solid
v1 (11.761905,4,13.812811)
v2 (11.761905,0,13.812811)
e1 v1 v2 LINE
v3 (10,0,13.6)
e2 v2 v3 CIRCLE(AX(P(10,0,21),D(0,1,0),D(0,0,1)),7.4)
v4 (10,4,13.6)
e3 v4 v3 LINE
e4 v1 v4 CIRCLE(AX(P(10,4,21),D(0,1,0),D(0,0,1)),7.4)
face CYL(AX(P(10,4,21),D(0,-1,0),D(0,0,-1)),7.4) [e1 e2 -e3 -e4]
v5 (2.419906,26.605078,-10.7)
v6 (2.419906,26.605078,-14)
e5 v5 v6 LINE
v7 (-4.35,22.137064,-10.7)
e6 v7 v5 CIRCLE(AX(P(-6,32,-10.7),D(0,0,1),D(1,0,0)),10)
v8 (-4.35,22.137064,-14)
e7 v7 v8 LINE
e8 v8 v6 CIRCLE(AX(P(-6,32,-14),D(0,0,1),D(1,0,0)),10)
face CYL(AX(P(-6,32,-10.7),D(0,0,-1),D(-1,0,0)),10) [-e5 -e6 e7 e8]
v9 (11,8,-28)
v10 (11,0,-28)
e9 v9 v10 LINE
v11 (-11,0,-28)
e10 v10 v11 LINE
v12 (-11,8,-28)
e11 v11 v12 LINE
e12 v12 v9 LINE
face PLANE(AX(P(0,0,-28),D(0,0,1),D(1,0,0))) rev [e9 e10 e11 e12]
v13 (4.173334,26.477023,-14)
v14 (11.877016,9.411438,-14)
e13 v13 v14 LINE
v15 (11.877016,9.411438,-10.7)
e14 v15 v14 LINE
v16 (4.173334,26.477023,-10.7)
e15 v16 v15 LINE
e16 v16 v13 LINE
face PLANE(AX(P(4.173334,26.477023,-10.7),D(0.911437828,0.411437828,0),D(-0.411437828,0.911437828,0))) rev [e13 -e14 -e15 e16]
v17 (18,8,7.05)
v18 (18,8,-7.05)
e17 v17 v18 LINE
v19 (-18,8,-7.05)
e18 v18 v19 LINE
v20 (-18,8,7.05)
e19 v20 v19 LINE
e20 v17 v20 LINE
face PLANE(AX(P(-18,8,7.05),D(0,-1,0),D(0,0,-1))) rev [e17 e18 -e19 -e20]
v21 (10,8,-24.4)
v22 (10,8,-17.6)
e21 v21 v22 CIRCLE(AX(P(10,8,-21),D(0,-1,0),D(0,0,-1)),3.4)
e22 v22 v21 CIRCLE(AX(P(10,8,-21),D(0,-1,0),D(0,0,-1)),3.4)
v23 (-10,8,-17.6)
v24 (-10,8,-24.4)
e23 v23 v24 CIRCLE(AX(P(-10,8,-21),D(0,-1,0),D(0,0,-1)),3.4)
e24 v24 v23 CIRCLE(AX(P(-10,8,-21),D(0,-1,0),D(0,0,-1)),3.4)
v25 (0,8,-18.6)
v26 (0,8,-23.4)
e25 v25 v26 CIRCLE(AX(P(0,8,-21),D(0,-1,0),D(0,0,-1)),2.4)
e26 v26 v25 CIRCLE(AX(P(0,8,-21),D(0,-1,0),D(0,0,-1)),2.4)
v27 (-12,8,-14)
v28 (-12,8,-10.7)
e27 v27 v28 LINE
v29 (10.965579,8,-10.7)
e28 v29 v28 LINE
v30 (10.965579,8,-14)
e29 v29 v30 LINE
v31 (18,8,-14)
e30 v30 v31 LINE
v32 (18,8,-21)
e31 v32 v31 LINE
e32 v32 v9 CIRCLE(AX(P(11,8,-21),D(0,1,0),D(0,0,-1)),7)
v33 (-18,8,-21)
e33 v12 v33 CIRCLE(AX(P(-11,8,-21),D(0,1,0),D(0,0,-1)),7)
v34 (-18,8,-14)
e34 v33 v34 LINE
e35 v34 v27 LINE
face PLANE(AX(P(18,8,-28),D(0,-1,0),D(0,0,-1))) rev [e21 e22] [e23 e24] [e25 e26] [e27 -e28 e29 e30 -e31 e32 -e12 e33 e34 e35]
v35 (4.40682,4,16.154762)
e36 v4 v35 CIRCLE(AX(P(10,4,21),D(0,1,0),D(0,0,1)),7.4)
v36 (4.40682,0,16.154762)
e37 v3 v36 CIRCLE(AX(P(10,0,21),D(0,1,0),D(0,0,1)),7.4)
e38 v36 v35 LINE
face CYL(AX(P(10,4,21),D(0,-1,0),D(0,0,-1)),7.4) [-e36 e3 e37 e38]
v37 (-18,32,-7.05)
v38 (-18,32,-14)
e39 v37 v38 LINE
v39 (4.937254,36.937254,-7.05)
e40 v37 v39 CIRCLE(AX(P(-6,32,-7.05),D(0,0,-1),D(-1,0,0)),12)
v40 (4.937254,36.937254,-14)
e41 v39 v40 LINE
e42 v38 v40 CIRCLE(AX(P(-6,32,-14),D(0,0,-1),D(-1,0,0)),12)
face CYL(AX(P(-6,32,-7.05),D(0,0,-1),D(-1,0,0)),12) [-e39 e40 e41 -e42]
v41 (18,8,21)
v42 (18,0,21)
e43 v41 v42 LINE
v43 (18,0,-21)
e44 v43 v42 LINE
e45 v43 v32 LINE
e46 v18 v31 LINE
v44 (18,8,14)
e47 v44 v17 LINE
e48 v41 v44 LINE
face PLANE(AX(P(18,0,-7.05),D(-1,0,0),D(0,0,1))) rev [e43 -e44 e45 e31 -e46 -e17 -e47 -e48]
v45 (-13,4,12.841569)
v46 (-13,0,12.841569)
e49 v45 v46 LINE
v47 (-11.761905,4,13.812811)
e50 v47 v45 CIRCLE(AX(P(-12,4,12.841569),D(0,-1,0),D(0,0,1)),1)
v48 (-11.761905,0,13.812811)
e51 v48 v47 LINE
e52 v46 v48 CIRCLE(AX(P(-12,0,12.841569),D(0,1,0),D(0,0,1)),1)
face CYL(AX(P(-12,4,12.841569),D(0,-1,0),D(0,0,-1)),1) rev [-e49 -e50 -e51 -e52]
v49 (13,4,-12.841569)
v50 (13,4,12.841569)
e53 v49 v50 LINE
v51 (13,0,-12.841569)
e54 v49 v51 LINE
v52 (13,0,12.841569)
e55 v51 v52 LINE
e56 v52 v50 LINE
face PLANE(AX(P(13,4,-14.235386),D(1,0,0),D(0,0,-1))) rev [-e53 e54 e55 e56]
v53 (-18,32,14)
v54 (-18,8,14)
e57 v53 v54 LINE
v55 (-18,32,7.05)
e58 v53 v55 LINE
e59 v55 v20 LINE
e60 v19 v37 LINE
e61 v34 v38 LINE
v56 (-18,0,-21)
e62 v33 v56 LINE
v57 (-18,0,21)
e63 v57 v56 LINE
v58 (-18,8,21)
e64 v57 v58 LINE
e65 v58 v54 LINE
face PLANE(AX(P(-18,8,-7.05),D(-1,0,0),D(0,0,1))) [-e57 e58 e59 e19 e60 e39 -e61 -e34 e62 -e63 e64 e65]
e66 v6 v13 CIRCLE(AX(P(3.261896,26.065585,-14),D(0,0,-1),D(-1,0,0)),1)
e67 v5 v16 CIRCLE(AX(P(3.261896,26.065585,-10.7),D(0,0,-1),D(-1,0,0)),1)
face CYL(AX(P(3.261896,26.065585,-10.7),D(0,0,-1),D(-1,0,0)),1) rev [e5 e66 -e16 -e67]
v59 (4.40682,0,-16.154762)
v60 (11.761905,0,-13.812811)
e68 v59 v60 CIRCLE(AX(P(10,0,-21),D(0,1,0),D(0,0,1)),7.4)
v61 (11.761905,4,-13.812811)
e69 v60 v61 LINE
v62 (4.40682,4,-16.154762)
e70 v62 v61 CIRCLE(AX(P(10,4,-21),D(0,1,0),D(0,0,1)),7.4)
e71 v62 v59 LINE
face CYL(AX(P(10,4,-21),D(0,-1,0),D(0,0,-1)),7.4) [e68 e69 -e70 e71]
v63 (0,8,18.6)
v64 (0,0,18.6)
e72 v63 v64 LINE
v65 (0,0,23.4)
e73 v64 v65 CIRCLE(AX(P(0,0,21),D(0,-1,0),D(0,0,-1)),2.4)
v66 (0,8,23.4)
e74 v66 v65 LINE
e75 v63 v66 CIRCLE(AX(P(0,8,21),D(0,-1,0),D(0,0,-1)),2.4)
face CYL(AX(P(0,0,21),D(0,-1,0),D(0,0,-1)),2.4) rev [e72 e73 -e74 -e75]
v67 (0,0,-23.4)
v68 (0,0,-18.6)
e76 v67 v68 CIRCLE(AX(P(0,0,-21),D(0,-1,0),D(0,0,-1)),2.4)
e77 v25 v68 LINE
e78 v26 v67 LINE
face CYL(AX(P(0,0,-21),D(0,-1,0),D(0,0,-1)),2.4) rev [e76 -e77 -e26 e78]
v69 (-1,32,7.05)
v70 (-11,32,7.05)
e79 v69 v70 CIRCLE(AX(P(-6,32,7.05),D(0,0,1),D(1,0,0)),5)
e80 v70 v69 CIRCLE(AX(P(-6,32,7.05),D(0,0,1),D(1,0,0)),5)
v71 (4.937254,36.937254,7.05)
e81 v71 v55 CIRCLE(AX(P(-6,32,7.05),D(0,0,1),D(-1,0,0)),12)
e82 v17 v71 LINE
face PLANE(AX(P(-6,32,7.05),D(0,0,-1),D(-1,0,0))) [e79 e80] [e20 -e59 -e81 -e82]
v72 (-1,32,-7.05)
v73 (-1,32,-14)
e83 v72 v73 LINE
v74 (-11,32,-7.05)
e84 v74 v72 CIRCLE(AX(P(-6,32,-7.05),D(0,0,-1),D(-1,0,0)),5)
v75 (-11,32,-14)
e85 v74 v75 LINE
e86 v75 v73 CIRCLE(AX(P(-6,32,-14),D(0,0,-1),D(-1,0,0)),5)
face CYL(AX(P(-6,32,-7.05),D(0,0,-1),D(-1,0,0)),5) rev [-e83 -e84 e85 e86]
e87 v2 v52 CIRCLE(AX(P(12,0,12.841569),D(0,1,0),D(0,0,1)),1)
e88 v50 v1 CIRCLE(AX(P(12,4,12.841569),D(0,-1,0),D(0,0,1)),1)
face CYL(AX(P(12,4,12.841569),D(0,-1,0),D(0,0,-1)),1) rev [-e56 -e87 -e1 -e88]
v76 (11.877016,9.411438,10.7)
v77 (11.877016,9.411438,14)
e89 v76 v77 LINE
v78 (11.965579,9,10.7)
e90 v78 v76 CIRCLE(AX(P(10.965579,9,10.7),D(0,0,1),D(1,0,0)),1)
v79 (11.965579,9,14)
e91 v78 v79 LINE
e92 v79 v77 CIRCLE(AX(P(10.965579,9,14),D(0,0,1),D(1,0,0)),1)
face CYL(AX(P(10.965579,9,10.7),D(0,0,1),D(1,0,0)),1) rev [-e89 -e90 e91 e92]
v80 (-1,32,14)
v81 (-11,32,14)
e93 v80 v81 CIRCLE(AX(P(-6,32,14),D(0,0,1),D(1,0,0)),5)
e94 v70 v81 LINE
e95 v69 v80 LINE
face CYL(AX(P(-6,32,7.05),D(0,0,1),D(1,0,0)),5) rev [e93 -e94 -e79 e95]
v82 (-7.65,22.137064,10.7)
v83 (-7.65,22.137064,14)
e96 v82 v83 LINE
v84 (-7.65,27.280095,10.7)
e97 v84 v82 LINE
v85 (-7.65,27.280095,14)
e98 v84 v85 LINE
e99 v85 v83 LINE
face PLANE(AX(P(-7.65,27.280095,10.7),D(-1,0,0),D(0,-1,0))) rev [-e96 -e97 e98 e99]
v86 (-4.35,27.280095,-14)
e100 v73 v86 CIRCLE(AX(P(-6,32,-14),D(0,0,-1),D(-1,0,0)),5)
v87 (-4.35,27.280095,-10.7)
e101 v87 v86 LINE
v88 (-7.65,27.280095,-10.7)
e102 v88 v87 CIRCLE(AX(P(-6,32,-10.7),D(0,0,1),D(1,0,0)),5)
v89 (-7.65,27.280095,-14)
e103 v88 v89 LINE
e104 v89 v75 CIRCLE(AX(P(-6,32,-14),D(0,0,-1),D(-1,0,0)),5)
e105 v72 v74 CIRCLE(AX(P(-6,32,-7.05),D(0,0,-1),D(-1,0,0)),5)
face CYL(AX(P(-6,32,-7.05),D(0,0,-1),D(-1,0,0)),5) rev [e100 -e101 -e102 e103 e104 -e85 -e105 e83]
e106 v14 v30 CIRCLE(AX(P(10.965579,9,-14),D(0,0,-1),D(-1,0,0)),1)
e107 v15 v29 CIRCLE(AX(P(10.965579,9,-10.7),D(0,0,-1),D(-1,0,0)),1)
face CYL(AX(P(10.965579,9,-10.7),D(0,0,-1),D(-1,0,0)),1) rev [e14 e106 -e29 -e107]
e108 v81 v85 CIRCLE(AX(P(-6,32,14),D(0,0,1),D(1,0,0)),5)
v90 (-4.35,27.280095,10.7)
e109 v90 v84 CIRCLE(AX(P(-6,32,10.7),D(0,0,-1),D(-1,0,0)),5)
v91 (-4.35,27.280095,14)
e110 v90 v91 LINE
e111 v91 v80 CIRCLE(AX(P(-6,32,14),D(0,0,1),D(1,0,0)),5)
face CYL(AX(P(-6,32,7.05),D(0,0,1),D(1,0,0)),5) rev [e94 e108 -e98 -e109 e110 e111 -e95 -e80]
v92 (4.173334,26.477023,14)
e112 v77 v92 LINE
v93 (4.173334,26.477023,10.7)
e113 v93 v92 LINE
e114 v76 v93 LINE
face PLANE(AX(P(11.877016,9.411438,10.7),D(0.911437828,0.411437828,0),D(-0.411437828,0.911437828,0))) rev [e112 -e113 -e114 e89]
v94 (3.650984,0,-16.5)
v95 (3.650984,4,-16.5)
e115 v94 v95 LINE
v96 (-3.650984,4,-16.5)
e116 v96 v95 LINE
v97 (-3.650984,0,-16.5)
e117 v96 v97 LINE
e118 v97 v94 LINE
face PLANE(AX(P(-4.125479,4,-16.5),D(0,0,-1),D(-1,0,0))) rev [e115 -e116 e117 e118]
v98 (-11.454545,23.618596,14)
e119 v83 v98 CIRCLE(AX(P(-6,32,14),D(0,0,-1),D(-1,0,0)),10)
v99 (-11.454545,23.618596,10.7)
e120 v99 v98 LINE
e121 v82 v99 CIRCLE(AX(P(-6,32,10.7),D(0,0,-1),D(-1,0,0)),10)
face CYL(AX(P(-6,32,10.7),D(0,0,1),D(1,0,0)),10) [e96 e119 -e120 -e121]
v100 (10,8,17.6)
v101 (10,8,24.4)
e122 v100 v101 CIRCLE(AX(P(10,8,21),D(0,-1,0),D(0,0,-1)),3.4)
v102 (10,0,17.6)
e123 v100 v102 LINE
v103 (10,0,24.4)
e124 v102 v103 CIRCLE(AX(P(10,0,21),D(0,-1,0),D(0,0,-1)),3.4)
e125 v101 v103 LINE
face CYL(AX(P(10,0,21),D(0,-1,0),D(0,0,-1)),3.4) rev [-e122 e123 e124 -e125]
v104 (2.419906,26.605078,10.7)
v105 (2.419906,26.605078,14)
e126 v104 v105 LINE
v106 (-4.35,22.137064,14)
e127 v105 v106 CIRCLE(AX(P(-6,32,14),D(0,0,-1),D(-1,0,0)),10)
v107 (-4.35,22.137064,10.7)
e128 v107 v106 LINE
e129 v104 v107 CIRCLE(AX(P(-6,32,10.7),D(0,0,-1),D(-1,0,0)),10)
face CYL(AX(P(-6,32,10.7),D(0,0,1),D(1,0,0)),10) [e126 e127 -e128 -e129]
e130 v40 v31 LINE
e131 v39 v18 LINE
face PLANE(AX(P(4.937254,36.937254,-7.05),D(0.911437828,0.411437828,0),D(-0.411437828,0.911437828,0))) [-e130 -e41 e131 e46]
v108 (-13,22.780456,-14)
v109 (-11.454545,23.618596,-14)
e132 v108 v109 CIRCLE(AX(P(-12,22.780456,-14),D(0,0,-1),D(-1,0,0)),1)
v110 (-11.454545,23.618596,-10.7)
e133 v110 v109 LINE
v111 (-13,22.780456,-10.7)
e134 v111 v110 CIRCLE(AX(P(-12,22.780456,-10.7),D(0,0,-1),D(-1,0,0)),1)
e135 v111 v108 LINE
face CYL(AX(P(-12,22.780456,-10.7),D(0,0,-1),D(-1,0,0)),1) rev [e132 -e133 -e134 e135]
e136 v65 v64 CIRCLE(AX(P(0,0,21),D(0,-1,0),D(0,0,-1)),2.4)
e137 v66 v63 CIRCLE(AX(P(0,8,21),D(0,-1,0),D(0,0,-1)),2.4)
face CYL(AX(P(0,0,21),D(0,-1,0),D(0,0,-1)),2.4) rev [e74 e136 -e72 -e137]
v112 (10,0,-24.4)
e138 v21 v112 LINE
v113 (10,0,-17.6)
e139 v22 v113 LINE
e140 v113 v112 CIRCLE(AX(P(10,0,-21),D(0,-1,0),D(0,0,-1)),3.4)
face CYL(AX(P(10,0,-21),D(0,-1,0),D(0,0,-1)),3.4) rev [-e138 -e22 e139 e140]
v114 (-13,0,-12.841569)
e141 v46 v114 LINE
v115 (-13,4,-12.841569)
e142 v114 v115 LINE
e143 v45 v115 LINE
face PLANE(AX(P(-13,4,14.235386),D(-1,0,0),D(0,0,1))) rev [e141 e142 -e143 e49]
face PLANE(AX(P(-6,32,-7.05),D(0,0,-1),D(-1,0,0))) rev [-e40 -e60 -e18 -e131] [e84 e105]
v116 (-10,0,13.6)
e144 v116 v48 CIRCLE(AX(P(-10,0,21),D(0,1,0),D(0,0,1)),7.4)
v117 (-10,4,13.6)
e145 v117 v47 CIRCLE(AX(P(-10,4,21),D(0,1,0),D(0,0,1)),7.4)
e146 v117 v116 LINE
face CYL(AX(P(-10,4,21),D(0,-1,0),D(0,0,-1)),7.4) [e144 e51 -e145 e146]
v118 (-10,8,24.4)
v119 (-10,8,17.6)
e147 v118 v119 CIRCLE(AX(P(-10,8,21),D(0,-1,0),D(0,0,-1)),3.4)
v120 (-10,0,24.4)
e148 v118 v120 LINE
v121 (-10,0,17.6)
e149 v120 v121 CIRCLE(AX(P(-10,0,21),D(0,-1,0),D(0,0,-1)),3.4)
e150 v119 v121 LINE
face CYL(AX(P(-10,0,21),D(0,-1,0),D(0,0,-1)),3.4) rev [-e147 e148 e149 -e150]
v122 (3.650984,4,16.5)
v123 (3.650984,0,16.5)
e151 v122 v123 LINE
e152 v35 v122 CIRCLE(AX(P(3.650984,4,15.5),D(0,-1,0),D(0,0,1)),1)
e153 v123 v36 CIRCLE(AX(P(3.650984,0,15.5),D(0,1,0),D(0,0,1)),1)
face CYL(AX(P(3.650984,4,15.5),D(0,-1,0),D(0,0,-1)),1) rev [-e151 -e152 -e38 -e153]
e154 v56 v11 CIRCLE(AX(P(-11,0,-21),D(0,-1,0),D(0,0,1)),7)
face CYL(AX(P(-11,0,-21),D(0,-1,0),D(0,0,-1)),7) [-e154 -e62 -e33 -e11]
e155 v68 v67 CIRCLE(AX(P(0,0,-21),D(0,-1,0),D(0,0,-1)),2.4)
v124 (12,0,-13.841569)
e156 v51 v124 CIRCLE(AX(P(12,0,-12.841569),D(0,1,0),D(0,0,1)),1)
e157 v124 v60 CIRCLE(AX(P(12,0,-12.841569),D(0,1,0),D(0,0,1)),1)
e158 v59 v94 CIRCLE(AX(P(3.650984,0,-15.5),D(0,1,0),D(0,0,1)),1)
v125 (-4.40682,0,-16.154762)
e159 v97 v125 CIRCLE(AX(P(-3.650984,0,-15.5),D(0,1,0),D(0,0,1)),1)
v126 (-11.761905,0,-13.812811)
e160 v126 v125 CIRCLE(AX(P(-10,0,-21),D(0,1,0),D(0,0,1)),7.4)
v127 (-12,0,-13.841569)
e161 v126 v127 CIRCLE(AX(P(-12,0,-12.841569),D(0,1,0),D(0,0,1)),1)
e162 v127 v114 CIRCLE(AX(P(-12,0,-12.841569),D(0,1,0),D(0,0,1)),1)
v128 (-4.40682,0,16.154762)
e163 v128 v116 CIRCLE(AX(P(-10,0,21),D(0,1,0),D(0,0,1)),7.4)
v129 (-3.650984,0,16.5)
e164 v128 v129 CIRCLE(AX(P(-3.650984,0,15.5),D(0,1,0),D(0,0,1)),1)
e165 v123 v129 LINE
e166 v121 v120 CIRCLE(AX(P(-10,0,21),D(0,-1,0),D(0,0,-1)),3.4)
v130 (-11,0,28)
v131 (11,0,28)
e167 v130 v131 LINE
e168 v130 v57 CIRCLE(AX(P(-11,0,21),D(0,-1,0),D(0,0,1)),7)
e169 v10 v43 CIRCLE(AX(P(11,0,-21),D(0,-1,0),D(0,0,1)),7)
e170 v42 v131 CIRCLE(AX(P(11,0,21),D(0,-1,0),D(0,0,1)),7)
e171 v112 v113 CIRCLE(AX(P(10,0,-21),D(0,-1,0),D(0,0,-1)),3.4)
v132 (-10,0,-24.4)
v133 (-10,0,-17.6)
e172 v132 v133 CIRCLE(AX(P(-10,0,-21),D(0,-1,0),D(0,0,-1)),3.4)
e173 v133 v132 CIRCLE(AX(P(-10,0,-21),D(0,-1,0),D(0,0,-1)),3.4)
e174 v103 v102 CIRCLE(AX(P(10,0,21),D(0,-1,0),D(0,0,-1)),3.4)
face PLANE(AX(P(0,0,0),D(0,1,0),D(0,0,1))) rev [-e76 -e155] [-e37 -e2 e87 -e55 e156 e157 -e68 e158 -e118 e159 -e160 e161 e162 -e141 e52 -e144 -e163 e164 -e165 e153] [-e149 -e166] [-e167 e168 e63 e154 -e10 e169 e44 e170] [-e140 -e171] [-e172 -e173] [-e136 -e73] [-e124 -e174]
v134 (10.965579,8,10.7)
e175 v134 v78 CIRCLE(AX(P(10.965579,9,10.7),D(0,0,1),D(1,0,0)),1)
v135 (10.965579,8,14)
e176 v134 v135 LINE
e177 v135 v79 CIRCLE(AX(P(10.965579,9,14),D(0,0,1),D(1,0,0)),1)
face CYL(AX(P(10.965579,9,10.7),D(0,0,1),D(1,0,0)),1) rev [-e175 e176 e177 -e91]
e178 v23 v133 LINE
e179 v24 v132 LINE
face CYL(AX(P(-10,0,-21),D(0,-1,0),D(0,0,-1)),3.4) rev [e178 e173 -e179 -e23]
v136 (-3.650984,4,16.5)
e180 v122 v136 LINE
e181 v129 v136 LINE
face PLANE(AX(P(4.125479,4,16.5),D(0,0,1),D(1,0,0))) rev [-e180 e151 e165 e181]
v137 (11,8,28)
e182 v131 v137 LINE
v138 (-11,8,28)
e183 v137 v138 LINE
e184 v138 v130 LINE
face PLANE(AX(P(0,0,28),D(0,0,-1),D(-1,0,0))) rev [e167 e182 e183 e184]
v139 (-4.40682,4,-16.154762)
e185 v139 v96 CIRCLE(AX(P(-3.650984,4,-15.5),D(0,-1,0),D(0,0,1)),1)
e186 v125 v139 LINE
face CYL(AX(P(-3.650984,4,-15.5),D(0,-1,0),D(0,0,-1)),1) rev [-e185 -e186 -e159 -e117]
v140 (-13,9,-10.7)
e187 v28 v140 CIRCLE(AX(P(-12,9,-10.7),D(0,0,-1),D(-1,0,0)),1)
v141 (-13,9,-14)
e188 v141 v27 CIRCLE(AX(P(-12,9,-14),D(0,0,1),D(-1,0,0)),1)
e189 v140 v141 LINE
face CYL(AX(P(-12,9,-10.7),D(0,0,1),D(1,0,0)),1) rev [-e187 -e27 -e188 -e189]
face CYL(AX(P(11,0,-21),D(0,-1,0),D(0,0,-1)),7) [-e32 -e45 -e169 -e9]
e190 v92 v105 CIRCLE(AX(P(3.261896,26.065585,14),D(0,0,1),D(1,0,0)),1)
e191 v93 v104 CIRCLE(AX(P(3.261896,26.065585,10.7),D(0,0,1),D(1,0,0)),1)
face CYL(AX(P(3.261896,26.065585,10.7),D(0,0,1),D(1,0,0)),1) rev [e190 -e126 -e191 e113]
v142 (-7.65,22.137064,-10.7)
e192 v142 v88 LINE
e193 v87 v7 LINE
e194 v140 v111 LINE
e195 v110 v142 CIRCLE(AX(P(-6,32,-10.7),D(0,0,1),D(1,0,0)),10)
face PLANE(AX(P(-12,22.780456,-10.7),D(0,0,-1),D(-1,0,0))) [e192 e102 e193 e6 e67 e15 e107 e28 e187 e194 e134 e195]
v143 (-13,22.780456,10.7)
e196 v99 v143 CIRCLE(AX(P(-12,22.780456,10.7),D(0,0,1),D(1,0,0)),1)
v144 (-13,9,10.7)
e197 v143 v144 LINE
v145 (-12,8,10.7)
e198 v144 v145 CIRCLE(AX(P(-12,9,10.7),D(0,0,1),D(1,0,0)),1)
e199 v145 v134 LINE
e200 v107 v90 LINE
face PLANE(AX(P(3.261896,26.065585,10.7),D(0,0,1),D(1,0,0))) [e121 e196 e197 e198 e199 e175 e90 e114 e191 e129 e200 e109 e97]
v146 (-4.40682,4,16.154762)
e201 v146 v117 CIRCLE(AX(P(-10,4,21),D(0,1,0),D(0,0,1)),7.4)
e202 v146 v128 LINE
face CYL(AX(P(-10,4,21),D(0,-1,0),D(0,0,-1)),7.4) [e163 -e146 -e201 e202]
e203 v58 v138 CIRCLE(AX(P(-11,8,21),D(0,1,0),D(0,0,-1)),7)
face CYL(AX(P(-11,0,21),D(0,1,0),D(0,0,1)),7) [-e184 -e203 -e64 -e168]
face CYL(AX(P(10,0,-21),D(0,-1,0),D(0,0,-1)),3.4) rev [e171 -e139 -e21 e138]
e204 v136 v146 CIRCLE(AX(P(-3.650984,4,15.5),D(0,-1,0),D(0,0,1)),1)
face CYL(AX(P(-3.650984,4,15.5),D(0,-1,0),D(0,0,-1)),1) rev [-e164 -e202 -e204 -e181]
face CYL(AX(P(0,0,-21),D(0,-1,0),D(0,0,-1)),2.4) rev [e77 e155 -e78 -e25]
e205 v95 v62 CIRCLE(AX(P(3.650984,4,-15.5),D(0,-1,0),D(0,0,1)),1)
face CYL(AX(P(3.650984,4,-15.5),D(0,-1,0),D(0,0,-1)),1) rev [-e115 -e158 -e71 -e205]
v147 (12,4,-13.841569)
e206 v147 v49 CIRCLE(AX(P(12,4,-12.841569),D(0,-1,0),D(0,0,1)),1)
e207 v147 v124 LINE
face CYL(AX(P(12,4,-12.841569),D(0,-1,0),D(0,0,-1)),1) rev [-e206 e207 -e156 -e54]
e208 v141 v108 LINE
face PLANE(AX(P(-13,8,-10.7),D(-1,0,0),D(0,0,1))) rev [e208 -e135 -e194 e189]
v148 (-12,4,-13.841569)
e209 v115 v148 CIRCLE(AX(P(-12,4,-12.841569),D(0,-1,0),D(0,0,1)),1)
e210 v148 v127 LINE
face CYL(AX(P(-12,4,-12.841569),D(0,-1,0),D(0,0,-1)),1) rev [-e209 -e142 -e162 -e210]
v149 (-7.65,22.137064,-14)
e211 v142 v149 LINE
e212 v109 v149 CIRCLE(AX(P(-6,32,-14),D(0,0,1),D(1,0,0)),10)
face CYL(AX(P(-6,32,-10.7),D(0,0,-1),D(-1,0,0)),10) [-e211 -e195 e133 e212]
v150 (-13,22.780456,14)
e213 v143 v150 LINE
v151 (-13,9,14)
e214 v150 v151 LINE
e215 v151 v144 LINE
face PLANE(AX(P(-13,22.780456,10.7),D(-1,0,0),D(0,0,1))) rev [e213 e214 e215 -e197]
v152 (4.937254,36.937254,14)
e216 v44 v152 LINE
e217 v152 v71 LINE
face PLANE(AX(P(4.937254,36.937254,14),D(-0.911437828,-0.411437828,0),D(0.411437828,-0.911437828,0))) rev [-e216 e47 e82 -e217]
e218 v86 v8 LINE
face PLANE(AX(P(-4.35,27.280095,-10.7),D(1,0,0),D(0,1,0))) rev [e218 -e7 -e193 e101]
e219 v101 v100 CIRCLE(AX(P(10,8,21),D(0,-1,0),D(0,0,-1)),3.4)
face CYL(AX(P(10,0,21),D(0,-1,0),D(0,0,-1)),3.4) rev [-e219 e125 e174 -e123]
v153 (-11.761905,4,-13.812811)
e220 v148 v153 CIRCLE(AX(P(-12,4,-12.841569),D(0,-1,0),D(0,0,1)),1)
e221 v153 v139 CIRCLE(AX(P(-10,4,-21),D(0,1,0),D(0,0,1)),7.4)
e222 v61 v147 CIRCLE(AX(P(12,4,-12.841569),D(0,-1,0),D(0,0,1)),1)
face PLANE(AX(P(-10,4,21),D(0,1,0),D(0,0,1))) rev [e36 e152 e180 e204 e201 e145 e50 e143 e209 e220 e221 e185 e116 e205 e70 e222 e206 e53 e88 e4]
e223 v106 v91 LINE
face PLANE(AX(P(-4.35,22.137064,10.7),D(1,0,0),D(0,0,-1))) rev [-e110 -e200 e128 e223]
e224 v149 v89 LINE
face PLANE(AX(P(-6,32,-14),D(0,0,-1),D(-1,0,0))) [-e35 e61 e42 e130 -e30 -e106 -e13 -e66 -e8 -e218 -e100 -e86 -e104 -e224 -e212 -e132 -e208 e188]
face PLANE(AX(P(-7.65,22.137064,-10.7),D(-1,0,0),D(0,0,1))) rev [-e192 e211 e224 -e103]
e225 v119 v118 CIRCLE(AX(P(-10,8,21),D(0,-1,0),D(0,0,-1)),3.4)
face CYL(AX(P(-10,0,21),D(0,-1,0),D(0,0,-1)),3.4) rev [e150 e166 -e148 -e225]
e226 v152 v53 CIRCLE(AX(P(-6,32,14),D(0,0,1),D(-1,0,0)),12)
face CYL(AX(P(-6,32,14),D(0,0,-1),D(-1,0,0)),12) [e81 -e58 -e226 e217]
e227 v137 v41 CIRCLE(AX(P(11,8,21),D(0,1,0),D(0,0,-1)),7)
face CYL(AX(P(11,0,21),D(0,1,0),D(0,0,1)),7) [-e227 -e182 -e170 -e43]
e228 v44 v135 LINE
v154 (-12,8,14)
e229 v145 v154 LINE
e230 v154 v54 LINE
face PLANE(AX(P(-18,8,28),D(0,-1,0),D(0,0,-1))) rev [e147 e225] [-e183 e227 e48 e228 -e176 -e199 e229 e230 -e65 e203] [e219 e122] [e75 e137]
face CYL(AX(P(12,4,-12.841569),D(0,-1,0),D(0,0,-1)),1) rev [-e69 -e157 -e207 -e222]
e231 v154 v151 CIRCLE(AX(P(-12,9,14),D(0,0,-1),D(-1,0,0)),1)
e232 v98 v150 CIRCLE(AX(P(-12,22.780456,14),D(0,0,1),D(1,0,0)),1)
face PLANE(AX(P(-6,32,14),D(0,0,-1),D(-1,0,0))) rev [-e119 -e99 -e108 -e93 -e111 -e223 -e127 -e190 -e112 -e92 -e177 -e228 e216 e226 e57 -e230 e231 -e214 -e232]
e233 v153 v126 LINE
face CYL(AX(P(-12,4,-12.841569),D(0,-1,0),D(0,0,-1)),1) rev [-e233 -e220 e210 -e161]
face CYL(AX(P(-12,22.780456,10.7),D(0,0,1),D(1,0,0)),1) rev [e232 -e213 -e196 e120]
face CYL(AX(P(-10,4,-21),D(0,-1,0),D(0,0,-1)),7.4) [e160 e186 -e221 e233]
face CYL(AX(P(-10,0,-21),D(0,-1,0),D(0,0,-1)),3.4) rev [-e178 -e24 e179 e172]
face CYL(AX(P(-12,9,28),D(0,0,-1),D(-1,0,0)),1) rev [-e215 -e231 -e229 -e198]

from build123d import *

# Parameters (mm, degrees)
EXTRUDE_1_DEPTH             = 6.95
SKETCH_2_W                  = 36
SKETCH_2_H                  = 6.95
EXTRUDE_2_DEPTH             = 8
SKETCH_3_W                  = 36
SKETCH_3_H                  = 8
EXTRUDE_3_DEPTH             = 14.1
EXTRUDE_4_DEPTH             = 6.95
SKETCH_5_W                  = 36
SKETCH_5_H                  = 8
EXTRUDE_5_DEPTH             = 14
CUT_EXTRUDE_1_DEPTH         = 3.3
SKETCH_7_W                  = 36
SKETCH_7_H                  = 8
EXTRUDE_6_DEPTH             = 14
CUT_EXTRUDE_START           = -3.3
CUT_EXTRUDE_2_DEPTH         = 3.3
CUT_EXTRUDE_3_DEPTH         = 3.3
CUT_EXTRUDE_4_DEPTH         = 3.3
CUT_EXTRUDE_5_DEPTH         = 4
SKETCH_12_W                 = 5
SKETCH_12_H                 = 6.95
SKETCH_13_W                 = 5
SKETCH_13_H                 = 6.95
HOLE_WIZARD_4_8_4_8_1_D     = 4.8
HOLE_WIZARD_4_8_4_8_1_DEPTH = 44
HOLE_WIZARD_6_8_6_8_1_D     = 6.8
HOLE_WIZARD_6_8_6_8_1_DEPTH = 44
FILLET_1_R                  = 1
FILLET_2_R                  = 7


with BuildPart() as part:
    # 草图1 → 凸台-拉伸1 (new body)
    with BuildSketch(Plane(origin=(0, 0, -14), x_dir=(-1, 0, 0), z_dir=(0, 0, -1))):
        with BuildLine():
            Line((-4.937253933, 36.937253933), (-18, 8))
            Line((-18, 8), (18, 8))
            Line((18, 8), (18, 32))
            ThreePointArc((18, 32), (8.525168589, 43.731305281), (-4.937253933, 36.937253933))
        make_face()
    extrude(amount=-EXTRUDE_1_DEPTH)

    # 草图2 → 凸台-拉伸2 (add)
    with BuildSketch(Plane.XZ.offset(-8)):
        with Locations((0, -10.525)):
            Rectangle(SKETCH_2_W, SKETCH_2_H)
    extrude(amount=EXTRUDE_2_DEPTH)

    # 草图3 → 凸台-拉伸3 (add)
    with BuildSketch(Plane.XY.offset(-7.05)):
        with Locations((0, 4)):
            Rectangle(SKETCH_3_W, SKETCH_3_H)
    extrude(amount=EXTRUDE_3_DEPTH)

    # 草图4 → 凸台-拉伸4 (add)
    with BuildSketch(Plane.XY.offset(7.05)):
        with BuildLine():
            Line((-18, 0), (-18, 32))
            ThreePointArc((-18, 32), (-8.525168589, 43.731305281), (4.937253933, 36.937253933))
            Line((4.937253933, 36.937253933), (18, 8))
            Line((18, 8), (18, 0))
            Line((18, 0), (-18, 0))
        make_face()
    extrude(amount=EXTRUDE_4_DEPTH)

    # 草图5 → 凸台-拉伸5 (add)
    with BuildSketch(Plane.XY.offset(14)):
        with Locations((0, 4)):
            Rectangle(SKETCH_5_W, SKETCH_5_H)
    extrude(amount=EXTRUDE_5_DEPTH)

    # 草图6 → 切除-拉伸1 (cut)
    with BuildSketch(Plane.XY.offset(14)):
        with BuildLine():
            Line((-13, 22.780455543), (-13, 8))
            Line((-13, 8), (10.965578526, 8))
            ThreePointArc((10.965578526, 8), (11.805649305, 8.457523193), (11.877016354, 9.411437828))
            Line((11.877016354, 9.411437828), (4.173334139, 26.477023221))
            ThreePointArc((4.173334139, 26.477023221), (3.334733206, 27.062929259), (2.419905737, 26.60507763))
            ThreePointArc((2.419905737, 26.60507763), (-3.895692843, 22.223912266), (-11.454545455, 23.618595948))
            ThreePointArc((-11.454545455, 23.618595948), (-12.476731295, 23.659504616), (-13, 22.780455543))
        make_face()
    extrude(amount=-CUT_EXTRUDE_1_DEPTH, mode=Mode.SUBTRACT)

    # 草图7 → 凸台-拉伸6 (add)
    with BuildSketch(Plane(origin=(0, 0, -14), x_dir=(-1, 0, 0), z_dir=(0, 0, -1))):
        with Locations((0, 4)):
            Rectangle(SKETCH_7_W, SKETCH_7_H)
    extrude(amount=EXTRUDE_6_DEPTH)

    # 草图8 → 切除-拉伸2 (cut)
    with BuildSketch(Plane(origin=(0, 0, -14), x_dir=(-1, 0, 0), z_dir=(0, 0, -1)).offset(CUT_EXTRUDE_START)):
        with BuildLine():
            Line((-4.173334139, 26.477023221), (-11.877016354, 9.411437828))
            ThreePointArc((-11.877016354, 9.411437828), (-11.805649305, 8.457523193), (-10.965578526, 8))
            Line((-10.965578526, 8), (13, 8))
            Line((13, 8), (13, 22.780455543))
            ThreePointArc((13, 22.780455543), (12.476731295, 23.659504616), (11.454545455, 23.618595948))
            ThreePointArc((11.454545455, 23.618595948), (3.895692843, 22.223912266), (-2.419905737, 26.60507763))
            ThreePointArc((-2.419905737, 26.60507763), (-3.334733206, 27.062929259), (-4.173334139, 26.477023221))
        make_face()
    extrude(amount=CUT_EXTRUDE_2_DEPTH, mode=Mode.SUBTRACT)

    # 草图9 → 切除-拉伸3 (cut)
    with BuildSketch(Plane.XY.offset(14)):
        with BuildLine():
            Line((-7.65, 27.28009534), (-7.65, 22.137064332))
            ThreePointArc((-7.65, 22.137064332), (-6, 22), (-4.35, 22.137064332))
            Line((-4.35, 22.137064332), (-4.35, 27.28009534))
            ThreePointArc((-4.35, 27.28009534), (-6, 27), (-7.65, 27.28009534))
        make_face()
    extrude(amount=-CUT_EXTRUDE_3_DEPTH, mode=Mode.SUBTRACT)

    # 草图10 → 切除-拉伸4 (cut)
    with BuildSketch(Plane(origin=(0, 0, -14), x_dir=(-1, 0, 0), z_dir=(0, 0, -1)).offset(CUT_EXTRUDE_START)):
        with BuildLine():
            Line((7.65, 22.137064332), (7.65, 27.28009534))
            ThreePointArc((7.65, 27.28009534), (6, 27), (4.35, 27.28009534))
            Line((4.35, 27.28009534), (4.35, 22.137064332))
            ThreePointArc((4.35, 22.137064332), (6, 22), (7.65, 22.137064332))
        make_face()
    extrude(amount=CUT_EXTRUDE_4_DEPTH, mode=Mode.SUBTRACT)

    # 草图11 → 切除-拉伸5 (cut)
    with BuildSketch(Plane.XZ):
        with BuildLine():
            Line((-13, 14.23538619), (-13, -14.23538619))
            ThreePointArc((-13, -14.23538619), (-8.170290449, -13.829772461), (-4.125478743, -16.5))
            Line((-4.125478743, -16.5), (4.125478743, -16.5))
            ThreePointArc((4.125478743, -16.5), (8.170290449, -13.829772461), (13, -14.23538619))
            Line((13, -14.23538619), (13, 14.23538619))
            ThreePointArc((13, 14.23538619), (8.170290449, 13.829772461), (4.125478743, 16.5))
            Line((4.125478743, 16.5), (-4.125478743, 16.5))
            ThreePointArc((-4.125478743, 16.5), (-8.170290449, 13.829772461), (-13, 14.23538619))
        make_face()
    extrude(amount=-CUT_EXTRUDE_5_DEPTH, mode=Mode.SUBTRACT)

    # 草图12 → 切除-旋转1 (revolve, cut)
    with BuildSketch(Plane(origin=(0, 32, 0), x_dir=(1, 0, 0), z_dir=(0, 1, 0))):
        with Locations((-3.5, -10.525)):
            Rectangle(SKETCH_12_W, SKETCH_12_H)
    revolve(axis=Axis((-6, 32, 7.05), (0, 0, 1)), mode=Mode.SUBTRACT)

    # 草图13 → 切除-旋转2 (revolve, cut)
    with BuildSketch(Plane.XZ.offset(-32), mode=Mode.PRIVATE) as cut_revolve_2_sk:
        with Locations((-3.5, -10.525)):
            Rectangle(SKETCH_13_W, SKETCH_13_H)
    revolve(cut_revolve_2_sk.sketch.rotate(Axis((-6, 32, -7.05), (0, 0, -1)), 180), axis=Axis((-6, 32, -7.05), (0, 0, -1)), mode=Mode.SUBTRACT)

    # Ø4.8 (4.8) 直径孔1
    with Locations(Plane(origin=(0, 0, 0), x_dir=(-1, 0, 0), z_dir=(0, -1, 0))):
        with Locations((0, 21), (0, -21)):
            Hole(HOLE_WIZARD_4_8_4_8_1_D / 2, depth=HOLE_WIZARD_4_8_4_8_1_DEPTH)

    # Ø6.8 (6.8) 直径孔1
    with Locations(Plane(origin=(0, 0, 0), x_dir=(-1, 0, 0), z_dir=(0, -1, 0))):
        with Locations((-10, 21), (-10, -21), (10, 21), (10, -21)):
            Hole(HOLE_WIZARD_6_8_6_8_1_D / 2, depth=HOLE_WIZARD_6_8_6_8_1_DEPTH)

    # 圆角1
    fillet_1_edges = [part.edges().sort_by_distance(p)[0] for p in [
        (-13, 8, -12.35),
        (-13, 2, 14.23538619),
        (-4.125478743, 2, 16.5),
        (4.125478743, 2, 16.5),
        (13, 2, 14.23538619),
        (13, 2, -14.23538619),
        (4.125478743, 2, -16.5),
        (-4.125478743, 2, -16.5),
        (-13, 2, -14.23538619),
        (-13, 8, 12.35),
    ]]
    fillet(fillet_1_edges, radius=FILLET_1_R)

    # 圆角2
    fillet_2_edges = [part.edges().sort_by_distance(p)[0] for p in [
        (-18, 4, 28),
        (18, 4, 28),
        (18, 4, -28),
        (-18, 4, -28),
    ]]
    fillet(fillet_2_edges, radius=FILLET_2_R)


solid = part.part
